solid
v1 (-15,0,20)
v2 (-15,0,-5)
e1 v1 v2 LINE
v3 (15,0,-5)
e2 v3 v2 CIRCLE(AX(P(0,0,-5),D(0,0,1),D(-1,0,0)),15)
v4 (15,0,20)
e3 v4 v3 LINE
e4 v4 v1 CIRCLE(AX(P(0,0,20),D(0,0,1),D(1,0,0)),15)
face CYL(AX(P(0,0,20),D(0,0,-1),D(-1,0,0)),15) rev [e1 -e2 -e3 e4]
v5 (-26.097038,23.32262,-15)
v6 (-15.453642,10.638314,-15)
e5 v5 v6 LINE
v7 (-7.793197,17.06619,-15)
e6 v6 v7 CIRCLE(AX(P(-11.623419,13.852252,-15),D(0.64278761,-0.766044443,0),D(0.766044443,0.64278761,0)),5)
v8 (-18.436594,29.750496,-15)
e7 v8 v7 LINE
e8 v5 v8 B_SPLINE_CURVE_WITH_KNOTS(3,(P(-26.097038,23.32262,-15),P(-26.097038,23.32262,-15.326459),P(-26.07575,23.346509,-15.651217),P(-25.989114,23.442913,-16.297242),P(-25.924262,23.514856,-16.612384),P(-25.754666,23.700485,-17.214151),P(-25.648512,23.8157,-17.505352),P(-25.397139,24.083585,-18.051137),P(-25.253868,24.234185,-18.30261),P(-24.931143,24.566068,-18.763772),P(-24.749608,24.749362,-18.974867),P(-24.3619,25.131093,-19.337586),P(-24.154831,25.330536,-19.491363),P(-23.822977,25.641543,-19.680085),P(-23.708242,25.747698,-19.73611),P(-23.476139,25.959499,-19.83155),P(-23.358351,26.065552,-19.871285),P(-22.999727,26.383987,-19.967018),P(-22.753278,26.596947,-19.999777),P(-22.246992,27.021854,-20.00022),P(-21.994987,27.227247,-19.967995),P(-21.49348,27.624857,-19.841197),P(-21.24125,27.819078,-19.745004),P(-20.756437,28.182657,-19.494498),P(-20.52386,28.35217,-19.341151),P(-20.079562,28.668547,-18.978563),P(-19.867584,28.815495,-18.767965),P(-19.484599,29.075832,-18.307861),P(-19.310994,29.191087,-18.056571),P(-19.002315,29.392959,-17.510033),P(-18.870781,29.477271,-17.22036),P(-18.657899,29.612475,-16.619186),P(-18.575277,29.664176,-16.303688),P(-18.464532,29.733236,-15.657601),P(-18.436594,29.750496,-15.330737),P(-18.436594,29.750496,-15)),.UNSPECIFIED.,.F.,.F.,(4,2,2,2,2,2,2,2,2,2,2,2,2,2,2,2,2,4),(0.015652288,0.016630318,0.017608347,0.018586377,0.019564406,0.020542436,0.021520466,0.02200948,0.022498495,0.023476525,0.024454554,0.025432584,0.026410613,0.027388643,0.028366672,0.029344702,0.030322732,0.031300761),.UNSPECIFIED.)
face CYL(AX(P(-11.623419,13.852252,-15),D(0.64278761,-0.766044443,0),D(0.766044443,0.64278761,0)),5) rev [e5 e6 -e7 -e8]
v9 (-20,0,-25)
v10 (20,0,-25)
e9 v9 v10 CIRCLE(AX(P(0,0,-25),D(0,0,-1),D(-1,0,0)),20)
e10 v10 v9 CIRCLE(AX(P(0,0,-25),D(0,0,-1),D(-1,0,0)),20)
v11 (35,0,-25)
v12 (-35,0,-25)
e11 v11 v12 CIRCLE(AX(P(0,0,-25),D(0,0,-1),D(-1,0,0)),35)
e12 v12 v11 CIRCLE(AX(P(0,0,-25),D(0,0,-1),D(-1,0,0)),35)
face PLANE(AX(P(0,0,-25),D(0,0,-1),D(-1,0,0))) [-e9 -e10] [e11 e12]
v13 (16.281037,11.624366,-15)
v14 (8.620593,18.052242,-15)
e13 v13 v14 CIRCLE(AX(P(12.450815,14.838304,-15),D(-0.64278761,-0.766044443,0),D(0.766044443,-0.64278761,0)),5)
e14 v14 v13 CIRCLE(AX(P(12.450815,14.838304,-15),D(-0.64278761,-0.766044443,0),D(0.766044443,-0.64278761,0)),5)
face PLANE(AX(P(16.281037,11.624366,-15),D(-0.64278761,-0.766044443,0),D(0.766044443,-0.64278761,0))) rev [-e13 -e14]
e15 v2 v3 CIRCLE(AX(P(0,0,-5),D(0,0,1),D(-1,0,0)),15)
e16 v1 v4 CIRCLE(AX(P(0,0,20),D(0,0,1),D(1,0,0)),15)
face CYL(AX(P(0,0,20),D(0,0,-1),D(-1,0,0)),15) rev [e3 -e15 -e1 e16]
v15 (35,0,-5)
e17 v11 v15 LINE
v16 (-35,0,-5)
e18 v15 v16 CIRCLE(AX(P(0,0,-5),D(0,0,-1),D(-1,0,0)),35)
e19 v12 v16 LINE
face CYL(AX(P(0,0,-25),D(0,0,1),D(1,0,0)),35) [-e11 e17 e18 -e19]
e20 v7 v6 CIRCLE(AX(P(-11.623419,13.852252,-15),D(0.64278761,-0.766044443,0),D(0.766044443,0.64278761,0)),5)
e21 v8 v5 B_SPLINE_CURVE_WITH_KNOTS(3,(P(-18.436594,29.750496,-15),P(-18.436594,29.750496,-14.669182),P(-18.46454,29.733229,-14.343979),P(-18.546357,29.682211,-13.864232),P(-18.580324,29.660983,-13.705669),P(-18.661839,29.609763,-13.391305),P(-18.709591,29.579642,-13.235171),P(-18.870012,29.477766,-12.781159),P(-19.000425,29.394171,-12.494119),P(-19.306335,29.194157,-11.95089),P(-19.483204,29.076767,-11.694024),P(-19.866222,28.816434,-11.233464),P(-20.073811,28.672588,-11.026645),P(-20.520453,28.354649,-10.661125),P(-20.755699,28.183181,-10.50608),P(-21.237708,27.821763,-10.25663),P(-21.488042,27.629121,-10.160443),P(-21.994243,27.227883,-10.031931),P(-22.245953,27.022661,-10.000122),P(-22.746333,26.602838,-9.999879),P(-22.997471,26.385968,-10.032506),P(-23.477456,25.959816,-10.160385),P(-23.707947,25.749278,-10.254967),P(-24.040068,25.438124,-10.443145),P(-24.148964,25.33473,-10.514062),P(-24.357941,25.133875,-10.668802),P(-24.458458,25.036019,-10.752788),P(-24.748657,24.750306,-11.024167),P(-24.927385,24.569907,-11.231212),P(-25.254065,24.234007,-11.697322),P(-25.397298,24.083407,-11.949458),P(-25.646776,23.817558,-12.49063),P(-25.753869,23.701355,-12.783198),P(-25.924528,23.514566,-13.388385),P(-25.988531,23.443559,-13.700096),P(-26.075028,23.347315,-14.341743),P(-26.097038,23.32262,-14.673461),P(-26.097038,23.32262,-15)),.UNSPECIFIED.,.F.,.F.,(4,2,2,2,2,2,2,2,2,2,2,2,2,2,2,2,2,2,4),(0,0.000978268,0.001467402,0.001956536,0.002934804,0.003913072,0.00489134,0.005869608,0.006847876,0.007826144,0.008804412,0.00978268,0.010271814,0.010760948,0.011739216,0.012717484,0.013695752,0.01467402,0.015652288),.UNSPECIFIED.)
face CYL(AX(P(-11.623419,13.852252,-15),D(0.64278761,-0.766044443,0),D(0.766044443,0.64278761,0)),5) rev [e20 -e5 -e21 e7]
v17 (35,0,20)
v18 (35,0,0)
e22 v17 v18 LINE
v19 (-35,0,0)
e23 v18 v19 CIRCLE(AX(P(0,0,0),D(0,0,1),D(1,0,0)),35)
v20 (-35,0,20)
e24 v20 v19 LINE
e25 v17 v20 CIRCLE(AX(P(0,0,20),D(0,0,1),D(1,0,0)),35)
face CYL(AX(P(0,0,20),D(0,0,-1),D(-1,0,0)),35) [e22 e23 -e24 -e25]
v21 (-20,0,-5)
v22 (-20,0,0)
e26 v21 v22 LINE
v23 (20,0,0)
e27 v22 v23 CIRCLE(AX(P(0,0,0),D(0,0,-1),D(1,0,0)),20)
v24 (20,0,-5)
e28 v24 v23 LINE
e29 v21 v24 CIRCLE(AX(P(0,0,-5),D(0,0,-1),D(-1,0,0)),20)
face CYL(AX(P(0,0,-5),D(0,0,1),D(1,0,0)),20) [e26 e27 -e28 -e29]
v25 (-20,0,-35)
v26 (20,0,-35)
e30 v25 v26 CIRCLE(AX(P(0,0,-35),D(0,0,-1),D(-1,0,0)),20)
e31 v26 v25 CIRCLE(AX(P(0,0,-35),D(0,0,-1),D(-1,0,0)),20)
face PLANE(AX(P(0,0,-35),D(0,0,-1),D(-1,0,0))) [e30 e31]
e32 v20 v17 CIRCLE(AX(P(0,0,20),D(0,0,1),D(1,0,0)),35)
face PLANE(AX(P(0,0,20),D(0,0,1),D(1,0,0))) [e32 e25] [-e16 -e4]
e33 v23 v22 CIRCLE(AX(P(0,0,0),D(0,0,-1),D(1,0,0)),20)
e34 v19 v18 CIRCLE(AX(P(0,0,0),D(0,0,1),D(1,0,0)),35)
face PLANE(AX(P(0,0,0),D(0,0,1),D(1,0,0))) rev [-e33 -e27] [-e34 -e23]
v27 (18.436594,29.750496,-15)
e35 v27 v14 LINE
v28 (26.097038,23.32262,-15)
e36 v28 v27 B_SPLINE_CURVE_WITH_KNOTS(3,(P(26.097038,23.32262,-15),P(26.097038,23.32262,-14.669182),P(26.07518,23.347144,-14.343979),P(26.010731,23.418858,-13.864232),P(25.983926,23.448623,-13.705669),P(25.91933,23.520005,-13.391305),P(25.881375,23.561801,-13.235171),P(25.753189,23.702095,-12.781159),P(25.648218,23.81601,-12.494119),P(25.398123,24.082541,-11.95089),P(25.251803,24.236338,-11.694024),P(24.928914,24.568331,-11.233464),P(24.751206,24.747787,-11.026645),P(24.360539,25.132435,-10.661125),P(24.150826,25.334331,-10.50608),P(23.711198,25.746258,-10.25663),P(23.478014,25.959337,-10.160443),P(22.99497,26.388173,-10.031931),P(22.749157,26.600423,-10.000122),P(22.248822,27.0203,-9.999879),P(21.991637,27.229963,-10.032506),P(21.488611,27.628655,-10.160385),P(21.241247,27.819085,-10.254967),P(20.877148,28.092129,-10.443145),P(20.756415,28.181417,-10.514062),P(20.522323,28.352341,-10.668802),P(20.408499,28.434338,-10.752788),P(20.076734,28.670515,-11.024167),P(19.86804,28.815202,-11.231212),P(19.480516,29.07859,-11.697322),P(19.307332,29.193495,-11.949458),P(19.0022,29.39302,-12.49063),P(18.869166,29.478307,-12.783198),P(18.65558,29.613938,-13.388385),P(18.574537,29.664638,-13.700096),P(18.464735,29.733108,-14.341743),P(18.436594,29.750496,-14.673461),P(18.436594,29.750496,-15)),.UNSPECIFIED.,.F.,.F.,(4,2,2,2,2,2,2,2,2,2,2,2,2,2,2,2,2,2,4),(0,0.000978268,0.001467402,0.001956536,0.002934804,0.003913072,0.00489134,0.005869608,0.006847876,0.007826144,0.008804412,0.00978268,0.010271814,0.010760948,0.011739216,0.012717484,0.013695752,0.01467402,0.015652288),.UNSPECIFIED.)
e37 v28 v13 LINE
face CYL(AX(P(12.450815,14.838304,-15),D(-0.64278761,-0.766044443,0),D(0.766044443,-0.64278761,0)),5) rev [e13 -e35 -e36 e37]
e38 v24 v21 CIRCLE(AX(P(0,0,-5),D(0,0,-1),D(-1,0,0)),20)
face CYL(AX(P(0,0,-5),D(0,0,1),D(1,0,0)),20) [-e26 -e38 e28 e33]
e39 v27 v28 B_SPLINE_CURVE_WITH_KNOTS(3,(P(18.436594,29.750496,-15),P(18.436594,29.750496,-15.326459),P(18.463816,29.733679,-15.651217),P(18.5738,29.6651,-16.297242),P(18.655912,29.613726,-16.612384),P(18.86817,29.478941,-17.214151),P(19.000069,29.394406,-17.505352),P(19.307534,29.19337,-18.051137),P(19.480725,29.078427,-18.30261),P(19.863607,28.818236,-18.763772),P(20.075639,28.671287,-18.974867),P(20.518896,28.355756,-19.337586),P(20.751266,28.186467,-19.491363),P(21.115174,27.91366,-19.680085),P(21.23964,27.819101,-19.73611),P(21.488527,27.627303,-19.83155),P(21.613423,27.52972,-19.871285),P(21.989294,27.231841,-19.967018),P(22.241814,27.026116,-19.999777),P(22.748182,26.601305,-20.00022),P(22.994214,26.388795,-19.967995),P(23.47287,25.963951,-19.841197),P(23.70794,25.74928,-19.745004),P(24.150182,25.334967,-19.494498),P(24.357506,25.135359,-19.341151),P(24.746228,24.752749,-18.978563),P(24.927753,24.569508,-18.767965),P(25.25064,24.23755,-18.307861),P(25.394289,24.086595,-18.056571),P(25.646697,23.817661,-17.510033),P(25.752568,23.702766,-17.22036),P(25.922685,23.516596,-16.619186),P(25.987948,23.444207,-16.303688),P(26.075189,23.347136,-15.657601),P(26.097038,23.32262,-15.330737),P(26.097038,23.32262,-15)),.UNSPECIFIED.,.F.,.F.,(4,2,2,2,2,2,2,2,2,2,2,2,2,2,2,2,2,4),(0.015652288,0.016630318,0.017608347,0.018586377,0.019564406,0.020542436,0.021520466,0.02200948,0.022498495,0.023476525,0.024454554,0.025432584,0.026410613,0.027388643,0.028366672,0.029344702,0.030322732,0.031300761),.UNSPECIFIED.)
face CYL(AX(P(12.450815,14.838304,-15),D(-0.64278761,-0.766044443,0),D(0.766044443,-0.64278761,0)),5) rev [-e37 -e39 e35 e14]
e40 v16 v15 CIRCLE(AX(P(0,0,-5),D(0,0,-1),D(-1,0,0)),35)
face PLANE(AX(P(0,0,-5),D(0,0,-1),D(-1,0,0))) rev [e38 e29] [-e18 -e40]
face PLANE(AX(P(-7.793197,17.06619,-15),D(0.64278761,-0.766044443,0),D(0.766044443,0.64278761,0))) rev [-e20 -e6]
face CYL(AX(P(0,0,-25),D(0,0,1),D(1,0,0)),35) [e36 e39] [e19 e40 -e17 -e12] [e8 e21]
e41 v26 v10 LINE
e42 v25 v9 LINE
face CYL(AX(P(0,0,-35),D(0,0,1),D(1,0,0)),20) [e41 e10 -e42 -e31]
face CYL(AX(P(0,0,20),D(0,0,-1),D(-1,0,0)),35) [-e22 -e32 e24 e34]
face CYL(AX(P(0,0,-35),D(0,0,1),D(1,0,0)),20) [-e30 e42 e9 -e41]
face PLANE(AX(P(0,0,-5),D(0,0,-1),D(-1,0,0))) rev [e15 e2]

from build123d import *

# Parameters (mm, degrees)
SKETCH1_R           = 35
SKETCH1_R_2         = 15
BOSS_EXTRUDE1_DEPTH = 20
SKETCH2_R           = 20
SKETCH2_R_2         = 15
BOSS_EXTRUDE2_DEPTH = 5
BOSS_EXTRUDE3_START = 20
SKETCH5_R           = 35
BOSS_EXTRUDE3_DEPTH = 20
BOSS_EXTRUDE4_START = 10
SKETCH6_R           = 20
BOSS_EXTRUDE4_DEPTH = 10


with BuildPart() as part:
    # Sketch1 → Boss-Extrude1 (new body)
    with BuildSketch(Plane.XY):
        Circle(SKETCH1_R)
        Circle(SKETCH1_R_2, mode=Mode.SUBTRACT)
    extrude(amount=BOSS_EXTRUDE1_DEPTH)

    # Sketch2 → Boss-Extrude2 (add, symmetric)
    with BuildSketch(Plane(origin=(0, 0, 0), x_dir=(-1, 0, 0), z_dir=(0, 0, -1))):
        with Locations(Location((0, 0, 0), (0, 0, 180))):
            Circle(SKETCH2_R)
        Circle(SKETCH2_R_2, mode=Mode.SUBTRACT)
    extrude(amount=BOSS_EXTRUDE2_DEPTH, both=True)

    # Sketch5 → Boss-Extrude3 (add)
    with BuildSketch(Plane(origin=(0, 0, -5), x_dir=(-1, 0, 0), z_dir=(0, 0, -1)).offset(BOSS_EXTRUDE3_START)):
        with Locations(Location((0, 0, 0), (0, 0, 180))):
            Circle(SKETCH5_R)
    extrude(amount=-BOSS_EXTRUDE3_DEPTH)

    # Sketch6 → Boss-Extrude4 (add)
    with BuildSketch(Plane(origin=(0, 0, -25), x_dir=(-1, 0, 0), z_dir=(0, 0, -1)).offset(BOSS_EXTRUDE4_START)):
        with Locations(Location((0, 0, 0), (0, 0, 180))):
            Circle(SKETCH6_R)
    extrude(amount=-BOSS_EXTRUDE4_DEPTH)

    # Sketch11 → Cut-Revolve2 (revolve, cut)
    with BuildSketch(Plane.XY.offset(-15)):
        Polygon((-11.623419421, 13.852251853), (-23.246838841, 27.704503705), (-19.416616626, 30.918441754), (-7.793197205, 17.066189901), align=None)
    revolve(axis=Axis((-11.623419421, 13.852251853, -15), (-0.642787609686535, 0.7660444431189817, 0)), mode=Mode.SUBTRACT)

    # Sketch17 → Cut-Revolve3 (revolve, cut)
    with BuildSketch(Plane.XY.offset(-15)):
        Polygon((12.450815126, 14.838303658), (24.416664753, 29.098647939), (28.246886969, 25.88470989), (16.281037342, 11.624365609), align=None)
    revolve(axis=Axis((12.450815126, 14.838303658, -15), (0.6427876096865406, 0.766044443118977, 0)), mode=Mode.SUBTRACT)


solid = part.part
